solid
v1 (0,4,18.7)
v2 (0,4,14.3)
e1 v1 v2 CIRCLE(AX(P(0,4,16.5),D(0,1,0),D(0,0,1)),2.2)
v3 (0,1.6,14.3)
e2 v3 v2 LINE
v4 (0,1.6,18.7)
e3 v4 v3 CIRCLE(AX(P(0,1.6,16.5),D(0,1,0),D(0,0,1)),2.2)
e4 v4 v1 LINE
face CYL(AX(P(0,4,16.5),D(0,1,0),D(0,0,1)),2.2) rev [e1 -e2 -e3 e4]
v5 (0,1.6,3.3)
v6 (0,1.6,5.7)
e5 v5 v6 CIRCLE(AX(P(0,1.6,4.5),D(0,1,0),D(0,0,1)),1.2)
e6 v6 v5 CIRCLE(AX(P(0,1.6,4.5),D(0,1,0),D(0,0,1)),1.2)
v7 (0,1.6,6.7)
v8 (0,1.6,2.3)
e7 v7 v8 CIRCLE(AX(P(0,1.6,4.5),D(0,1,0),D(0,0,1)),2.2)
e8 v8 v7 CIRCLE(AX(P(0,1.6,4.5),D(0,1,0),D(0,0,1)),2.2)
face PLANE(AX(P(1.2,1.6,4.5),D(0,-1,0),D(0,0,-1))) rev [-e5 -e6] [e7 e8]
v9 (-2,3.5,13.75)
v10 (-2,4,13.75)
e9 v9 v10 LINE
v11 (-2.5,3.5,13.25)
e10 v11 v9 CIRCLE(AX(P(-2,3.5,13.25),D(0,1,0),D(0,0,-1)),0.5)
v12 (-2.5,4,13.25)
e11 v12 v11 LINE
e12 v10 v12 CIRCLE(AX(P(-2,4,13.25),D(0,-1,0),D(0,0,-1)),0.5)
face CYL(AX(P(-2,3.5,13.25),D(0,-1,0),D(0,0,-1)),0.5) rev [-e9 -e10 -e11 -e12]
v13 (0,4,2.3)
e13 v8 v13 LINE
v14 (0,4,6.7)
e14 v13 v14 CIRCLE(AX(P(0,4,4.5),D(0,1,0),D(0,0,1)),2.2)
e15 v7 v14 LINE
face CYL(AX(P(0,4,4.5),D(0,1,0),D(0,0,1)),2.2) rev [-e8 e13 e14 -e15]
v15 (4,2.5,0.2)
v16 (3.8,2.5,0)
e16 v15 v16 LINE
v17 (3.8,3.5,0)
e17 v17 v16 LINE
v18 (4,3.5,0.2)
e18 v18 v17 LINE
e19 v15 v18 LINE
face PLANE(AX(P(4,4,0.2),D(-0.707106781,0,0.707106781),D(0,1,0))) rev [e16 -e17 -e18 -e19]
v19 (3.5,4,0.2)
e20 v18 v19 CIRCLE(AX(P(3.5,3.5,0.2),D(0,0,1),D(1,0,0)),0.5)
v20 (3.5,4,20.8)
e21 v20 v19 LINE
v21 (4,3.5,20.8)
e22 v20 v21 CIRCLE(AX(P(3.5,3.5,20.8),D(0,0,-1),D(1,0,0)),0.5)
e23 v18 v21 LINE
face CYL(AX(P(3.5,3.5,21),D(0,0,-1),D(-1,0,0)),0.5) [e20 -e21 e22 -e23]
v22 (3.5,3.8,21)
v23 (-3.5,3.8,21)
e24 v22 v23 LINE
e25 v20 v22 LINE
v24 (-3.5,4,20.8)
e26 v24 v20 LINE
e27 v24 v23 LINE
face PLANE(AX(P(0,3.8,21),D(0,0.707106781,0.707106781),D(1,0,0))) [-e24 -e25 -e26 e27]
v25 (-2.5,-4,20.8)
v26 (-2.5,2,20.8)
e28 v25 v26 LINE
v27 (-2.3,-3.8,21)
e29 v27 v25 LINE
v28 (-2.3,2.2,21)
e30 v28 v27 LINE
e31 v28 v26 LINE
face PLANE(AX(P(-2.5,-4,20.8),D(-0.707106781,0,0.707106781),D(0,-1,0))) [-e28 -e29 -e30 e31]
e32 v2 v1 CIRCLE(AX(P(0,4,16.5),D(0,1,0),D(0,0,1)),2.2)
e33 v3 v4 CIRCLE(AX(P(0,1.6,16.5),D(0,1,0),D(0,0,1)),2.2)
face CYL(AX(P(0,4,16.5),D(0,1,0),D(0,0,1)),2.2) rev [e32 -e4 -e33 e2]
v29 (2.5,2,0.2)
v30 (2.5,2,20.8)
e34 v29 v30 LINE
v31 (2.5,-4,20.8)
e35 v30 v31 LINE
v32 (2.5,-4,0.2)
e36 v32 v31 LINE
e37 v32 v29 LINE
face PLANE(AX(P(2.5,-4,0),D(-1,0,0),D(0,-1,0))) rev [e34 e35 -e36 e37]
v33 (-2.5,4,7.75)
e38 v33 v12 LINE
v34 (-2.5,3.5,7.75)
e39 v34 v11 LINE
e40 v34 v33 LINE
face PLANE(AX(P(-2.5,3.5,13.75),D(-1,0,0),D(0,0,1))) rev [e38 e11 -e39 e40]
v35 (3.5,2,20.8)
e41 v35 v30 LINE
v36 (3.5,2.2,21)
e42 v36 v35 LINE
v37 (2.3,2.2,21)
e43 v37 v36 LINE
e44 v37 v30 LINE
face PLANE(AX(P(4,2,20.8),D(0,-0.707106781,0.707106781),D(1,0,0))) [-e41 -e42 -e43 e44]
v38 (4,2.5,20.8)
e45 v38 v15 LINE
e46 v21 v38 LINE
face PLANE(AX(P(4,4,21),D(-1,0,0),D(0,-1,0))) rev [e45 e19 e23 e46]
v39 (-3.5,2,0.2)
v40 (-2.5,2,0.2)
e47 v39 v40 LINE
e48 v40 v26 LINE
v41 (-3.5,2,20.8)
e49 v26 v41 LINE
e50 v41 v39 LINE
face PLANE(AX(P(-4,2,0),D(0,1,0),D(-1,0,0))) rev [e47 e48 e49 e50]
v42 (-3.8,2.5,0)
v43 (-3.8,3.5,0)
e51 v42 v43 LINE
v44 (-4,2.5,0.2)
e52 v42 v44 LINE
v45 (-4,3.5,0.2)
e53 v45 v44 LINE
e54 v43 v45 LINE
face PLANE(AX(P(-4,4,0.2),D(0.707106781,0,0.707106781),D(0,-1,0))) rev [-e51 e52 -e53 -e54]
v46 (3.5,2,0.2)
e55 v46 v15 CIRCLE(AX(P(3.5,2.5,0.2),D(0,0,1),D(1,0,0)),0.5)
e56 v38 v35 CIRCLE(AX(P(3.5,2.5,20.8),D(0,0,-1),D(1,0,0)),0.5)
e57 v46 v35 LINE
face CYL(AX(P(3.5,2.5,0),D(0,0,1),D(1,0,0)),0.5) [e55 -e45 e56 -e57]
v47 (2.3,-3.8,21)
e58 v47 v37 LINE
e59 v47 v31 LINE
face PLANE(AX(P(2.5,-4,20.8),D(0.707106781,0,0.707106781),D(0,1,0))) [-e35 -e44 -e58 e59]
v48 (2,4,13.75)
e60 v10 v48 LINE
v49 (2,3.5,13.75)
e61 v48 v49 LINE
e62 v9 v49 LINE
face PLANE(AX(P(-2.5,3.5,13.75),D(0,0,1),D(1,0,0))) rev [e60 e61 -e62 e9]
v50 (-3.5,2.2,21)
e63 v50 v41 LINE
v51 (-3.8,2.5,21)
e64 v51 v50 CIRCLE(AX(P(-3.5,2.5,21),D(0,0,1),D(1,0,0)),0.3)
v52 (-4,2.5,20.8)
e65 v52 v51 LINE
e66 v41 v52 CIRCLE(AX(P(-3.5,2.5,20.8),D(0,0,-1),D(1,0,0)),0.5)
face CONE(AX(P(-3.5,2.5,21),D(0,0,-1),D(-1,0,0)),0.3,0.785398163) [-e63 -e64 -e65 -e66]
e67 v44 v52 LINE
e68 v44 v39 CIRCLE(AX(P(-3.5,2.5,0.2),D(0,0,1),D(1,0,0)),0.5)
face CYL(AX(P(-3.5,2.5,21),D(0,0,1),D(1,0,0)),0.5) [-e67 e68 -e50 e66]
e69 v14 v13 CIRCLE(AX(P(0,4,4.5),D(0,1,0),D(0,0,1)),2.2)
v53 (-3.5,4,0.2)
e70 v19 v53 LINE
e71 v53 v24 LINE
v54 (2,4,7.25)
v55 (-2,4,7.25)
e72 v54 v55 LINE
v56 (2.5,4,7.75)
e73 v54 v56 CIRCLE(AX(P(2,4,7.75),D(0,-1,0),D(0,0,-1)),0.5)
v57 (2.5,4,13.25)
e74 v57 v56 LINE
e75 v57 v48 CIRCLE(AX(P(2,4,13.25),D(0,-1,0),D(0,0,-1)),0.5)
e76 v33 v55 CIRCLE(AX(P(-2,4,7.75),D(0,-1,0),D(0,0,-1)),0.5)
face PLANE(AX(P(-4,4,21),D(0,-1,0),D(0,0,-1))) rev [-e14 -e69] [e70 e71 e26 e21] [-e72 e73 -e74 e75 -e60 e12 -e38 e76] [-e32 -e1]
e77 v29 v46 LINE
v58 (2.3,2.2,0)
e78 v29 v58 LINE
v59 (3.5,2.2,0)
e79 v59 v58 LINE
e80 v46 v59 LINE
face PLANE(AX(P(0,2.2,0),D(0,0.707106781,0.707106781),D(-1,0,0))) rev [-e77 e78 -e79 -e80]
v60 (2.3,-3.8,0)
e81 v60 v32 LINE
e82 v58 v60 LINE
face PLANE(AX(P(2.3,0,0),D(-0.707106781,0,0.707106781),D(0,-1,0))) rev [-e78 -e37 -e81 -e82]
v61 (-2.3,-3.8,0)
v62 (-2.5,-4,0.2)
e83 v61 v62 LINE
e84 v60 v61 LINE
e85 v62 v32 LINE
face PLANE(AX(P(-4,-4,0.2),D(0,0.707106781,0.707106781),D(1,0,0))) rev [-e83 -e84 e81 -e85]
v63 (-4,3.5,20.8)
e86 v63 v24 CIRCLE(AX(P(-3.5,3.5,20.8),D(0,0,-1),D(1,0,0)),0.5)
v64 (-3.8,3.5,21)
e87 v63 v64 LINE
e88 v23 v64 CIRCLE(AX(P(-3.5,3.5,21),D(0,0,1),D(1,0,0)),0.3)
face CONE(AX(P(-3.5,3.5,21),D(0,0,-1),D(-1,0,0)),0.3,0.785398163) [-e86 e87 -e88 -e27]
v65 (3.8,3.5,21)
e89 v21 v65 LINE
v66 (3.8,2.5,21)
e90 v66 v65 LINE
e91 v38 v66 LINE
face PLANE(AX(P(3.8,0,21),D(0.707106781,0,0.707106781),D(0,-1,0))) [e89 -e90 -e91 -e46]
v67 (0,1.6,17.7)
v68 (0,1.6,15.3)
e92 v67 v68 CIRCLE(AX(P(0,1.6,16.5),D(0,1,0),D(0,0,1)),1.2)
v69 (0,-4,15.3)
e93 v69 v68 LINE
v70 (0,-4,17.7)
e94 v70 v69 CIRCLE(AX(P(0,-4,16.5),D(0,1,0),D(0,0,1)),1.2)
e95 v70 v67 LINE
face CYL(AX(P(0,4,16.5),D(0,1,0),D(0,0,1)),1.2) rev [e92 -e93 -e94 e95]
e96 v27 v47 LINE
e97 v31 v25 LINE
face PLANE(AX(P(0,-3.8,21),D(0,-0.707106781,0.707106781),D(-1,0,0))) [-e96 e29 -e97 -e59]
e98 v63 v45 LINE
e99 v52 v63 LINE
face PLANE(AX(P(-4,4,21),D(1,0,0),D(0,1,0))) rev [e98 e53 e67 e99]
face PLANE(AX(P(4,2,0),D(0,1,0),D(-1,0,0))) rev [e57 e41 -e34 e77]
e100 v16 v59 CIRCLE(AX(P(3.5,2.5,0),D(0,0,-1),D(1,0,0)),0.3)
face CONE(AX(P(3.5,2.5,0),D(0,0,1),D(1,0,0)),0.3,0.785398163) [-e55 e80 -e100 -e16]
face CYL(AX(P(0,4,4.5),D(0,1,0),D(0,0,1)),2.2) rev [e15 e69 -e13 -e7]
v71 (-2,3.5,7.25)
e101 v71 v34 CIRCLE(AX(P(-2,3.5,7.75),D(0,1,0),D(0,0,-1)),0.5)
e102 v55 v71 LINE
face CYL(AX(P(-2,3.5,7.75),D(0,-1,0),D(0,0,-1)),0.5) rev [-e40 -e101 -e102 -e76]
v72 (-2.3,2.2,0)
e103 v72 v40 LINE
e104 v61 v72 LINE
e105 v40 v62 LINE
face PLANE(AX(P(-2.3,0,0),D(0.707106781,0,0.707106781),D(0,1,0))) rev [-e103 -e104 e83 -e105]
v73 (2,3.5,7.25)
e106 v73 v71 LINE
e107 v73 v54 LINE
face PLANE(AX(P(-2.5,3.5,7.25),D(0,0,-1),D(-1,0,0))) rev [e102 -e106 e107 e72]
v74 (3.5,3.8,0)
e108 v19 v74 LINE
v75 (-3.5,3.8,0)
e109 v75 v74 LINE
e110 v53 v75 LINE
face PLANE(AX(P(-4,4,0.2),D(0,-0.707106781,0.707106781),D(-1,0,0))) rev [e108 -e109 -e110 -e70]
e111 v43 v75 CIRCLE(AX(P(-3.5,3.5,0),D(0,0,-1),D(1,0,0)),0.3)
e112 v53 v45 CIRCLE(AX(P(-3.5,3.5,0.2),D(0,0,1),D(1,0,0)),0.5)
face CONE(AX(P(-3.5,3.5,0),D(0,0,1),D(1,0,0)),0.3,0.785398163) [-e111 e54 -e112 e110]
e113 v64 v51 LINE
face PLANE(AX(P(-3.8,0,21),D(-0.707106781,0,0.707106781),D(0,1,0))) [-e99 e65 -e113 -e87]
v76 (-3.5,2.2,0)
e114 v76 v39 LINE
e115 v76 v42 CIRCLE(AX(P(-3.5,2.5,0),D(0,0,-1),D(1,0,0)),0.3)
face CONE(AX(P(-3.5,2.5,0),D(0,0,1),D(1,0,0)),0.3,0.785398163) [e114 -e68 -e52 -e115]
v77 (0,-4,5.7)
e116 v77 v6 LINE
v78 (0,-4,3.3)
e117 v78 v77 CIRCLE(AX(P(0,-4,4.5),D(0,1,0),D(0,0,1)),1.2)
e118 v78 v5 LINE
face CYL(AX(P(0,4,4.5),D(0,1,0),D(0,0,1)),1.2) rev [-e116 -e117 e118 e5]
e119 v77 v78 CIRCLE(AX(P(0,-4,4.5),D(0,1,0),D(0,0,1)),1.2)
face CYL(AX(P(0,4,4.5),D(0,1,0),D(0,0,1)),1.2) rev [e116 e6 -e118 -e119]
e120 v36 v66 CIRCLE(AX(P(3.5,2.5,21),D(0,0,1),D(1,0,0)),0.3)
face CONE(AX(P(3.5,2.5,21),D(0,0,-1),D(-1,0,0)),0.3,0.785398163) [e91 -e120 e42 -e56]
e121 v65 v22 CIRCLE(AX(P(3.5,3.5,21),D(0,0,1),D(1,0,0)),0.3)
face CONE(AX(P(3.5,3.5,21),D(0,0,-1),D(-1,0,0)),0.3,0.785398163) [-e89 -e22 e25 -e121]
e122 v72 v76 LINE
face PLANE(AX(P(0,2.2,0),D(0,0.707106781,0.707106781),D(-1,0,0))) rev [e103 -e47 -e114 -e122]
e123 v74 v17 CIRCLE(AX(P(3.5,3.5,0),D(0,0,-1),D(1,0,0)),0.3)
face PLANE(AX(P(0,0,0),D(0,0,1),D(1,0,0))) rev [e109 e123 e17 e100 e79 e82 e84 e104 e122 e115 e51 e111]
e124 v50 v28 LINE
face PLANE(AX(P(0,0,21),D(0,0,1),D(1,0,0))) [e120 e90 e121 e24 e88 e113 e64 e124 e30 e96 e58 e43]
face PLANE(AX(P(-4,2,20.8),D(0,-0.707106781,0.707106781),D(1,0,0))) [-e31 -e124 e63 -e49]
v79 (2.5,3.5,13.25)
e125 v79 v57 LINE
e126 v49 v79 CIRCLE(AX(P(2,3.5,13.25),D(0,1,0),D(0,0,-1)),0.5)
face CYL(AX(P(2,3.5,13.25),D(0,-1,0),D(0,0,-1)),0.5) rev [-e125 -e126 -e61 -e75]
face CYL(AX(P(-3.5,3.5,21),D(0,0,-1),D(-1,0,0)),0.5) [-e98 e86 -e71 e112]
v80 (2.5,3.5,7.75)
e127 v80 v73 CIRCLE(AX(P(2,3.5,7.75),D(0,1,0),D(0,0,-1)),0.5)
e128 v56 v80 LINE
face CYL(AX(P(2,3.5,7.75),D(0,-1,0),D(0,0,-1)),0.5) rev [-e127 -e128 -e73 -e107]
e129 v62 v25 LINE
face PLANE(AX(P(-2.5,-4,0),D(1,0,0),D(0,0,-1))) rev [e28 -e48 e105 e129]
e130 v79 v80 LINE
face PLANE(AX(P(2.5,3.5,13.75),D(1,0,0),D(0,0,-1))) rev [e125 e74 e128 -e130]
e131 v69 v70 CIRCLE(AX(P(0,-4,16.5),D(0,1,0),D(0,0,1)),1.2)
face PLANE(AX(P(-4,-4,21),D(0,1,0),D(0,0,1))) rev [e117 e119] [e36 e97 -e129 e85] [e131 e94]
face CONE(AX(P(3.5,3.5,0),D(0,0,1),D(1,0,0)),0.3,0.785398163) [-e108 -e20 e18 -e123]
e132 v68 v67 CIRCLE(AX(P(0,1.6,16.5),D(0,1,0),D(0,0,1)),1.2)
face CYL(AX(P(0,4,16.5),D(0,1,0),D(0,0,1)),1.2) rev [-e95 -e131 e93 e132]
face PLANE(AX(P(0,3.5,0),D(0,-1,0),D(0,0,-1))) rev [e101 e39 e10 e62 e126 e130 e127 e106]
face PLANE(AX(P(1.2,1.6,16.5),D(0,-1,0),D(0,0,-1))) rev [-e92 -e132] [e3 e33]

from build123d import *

# Parameters (mm, degrees)
SKETCH1_W                                           = 8
SKETCH1_H                                           = 8
BOSS_EXTRUDE1_DEPTH                                 = 21
SKETCH2_W                                           = 1.5
SKETCH2_H                                           = 6
CUT_EXTRUDE1_DEPTH                                  = 22.748563171
FILLET1_R                                           = 0.5
CBORE_FOR_M2_HEX_SOCKET_HEAD_CAP_SCREW1_D           = 2.4
CBORE_FOR_M2_HEX_SOCKET_HEAD_CAP_SCREW1_CBORE_D     = 4.4
CBORE_FOR_M2_HEX_SOCKET_HEAD_CAP_SCREW1_CBORE_DEPTH = 2.4
CHAMFER1_SIZE                                       = 0.2
SKETCH7_W                                           = 5
SKETCH7_H                                           = 6.5
CUT_EXTRUDE2_DEPTH                                  = 0.5
FILLET2_R                                           = 0.5


with BuildPart() as part:
    # Sketch1 → Boss-Extrude1 (new body)
    with BuildSketch(Plane.XY):
        Rectangle(SKETCH1_W, SKETCH1_H)
    extrude(amount=BOSS_EXTRUDE1_DEPTH)

    # Sketch2 → Cut-Extrude1 (cut, through all)
    with BuildSketch(Plane.XY.offset(21)):
        with Locations((-3.25, -1)):
            Rectangle(SKETCH2_W, SKETCH2_H)
        with Locations((3.25, -1)):
            Rectangle(SKETCH2_W, SKETCH2_H)
    extrude(amount=-CUT_EXTRUDE1_DEPTH, mode=Mode.SUBTRACT)

    # Fillet1
    fillet1_edges = [part.edges().sort_by_distance(p)[0] for p in [
        (-4, 2, 10.5),
        (4, 2, 10.5),
        (-4, 4, 10.5),
        (4, 4, 10.5),
    ]]
    fillet(fillet1_edges, radius=FILLET1_R)

    # CBORE for M2 Hex Socket Head Cap Screw1 (through all)
    with Locations(Plane(origin=(0, 4, 0), x_dir=(1, 0, 0), z_dir=(0, 1, 0))):
        with Locations((0, -4.5), (0, -16.5)):
            CounterBoreHole(CBORE_FOR_M2_HEX_SOCKET_HEAD_CAP_SCREW1_D / 2, CBORE_FOR_M2_HEX_SOCKET_HEAD_CAP_SCREW1_CBORE_D / 2, CBORE_FOR_M2_HEX_SOCKET_HEAD_CAP_SCREW1_CBORE_DEPTH)

    # Chamfer1
    chamfer1_edges = [part.edges().sort_by_distance(p)[0] for p in [
        (0, -4, 0),
        (0, -4, 21),
        (-3, 2, 0),
        (-2.5, -1, 0),
        (-2.5, -1, 21),
        (-3, 2, 21),
        (2.5, -1, 0),
        (2.5, -1, 21),
        (0, 4, 0),
        (0, 4, 21),
        (-4, 3, 0),
        (4, 3, 0),
        (3, 2, 0),
        (-3.853553391, 2.146446609, 0),
        (-3.853553391, 3.853553391, 0),
        (3.853553391, 2.146446609, 0),
        (3.853553391, 3.853553391, 0),
        (4, 3, 21),
        (3, 2, 21),
        (-4, 3, 21),
        (-3.853553391, 2.146446609, 21),
        (-3.853553391, 3.853553391, 21),
        (3.853553391, 2.146446609, 21),
        (3.853553391, 3.853553391, 21),
    ]]
    chamfer(chamfer1_edges, length=CHAMFER1_SIZE)

    # Sketch7 → Cut-Extrude2 (cut)
    with BuildSketch(Plane(origin=(0, 4, 0), x_dir=(1, 0, 0), z_dir=(0, 1, 0))):
        with Locations((0, -10.5)):
            Rectangle(SKETCH7_W, SKETCH7_H)
    extrude(amount=-CUT_EXTRUDE2_DEPTH, mode=Mode.SUBTRACT)

    # Fillet2
    fillet2_edges = [part.edges().sort_by_distance(p)[0] for p in [
        (2.5, 3.75, 7.25),
        (2.5, 3.75, 13.75),
        (-2.5, 3.75, 13.75),
        (-2.5, 3.75, 7.25),
    ]]
    fillet(fillet2_edges, radius=FILLET2_R)


solid = part.part
